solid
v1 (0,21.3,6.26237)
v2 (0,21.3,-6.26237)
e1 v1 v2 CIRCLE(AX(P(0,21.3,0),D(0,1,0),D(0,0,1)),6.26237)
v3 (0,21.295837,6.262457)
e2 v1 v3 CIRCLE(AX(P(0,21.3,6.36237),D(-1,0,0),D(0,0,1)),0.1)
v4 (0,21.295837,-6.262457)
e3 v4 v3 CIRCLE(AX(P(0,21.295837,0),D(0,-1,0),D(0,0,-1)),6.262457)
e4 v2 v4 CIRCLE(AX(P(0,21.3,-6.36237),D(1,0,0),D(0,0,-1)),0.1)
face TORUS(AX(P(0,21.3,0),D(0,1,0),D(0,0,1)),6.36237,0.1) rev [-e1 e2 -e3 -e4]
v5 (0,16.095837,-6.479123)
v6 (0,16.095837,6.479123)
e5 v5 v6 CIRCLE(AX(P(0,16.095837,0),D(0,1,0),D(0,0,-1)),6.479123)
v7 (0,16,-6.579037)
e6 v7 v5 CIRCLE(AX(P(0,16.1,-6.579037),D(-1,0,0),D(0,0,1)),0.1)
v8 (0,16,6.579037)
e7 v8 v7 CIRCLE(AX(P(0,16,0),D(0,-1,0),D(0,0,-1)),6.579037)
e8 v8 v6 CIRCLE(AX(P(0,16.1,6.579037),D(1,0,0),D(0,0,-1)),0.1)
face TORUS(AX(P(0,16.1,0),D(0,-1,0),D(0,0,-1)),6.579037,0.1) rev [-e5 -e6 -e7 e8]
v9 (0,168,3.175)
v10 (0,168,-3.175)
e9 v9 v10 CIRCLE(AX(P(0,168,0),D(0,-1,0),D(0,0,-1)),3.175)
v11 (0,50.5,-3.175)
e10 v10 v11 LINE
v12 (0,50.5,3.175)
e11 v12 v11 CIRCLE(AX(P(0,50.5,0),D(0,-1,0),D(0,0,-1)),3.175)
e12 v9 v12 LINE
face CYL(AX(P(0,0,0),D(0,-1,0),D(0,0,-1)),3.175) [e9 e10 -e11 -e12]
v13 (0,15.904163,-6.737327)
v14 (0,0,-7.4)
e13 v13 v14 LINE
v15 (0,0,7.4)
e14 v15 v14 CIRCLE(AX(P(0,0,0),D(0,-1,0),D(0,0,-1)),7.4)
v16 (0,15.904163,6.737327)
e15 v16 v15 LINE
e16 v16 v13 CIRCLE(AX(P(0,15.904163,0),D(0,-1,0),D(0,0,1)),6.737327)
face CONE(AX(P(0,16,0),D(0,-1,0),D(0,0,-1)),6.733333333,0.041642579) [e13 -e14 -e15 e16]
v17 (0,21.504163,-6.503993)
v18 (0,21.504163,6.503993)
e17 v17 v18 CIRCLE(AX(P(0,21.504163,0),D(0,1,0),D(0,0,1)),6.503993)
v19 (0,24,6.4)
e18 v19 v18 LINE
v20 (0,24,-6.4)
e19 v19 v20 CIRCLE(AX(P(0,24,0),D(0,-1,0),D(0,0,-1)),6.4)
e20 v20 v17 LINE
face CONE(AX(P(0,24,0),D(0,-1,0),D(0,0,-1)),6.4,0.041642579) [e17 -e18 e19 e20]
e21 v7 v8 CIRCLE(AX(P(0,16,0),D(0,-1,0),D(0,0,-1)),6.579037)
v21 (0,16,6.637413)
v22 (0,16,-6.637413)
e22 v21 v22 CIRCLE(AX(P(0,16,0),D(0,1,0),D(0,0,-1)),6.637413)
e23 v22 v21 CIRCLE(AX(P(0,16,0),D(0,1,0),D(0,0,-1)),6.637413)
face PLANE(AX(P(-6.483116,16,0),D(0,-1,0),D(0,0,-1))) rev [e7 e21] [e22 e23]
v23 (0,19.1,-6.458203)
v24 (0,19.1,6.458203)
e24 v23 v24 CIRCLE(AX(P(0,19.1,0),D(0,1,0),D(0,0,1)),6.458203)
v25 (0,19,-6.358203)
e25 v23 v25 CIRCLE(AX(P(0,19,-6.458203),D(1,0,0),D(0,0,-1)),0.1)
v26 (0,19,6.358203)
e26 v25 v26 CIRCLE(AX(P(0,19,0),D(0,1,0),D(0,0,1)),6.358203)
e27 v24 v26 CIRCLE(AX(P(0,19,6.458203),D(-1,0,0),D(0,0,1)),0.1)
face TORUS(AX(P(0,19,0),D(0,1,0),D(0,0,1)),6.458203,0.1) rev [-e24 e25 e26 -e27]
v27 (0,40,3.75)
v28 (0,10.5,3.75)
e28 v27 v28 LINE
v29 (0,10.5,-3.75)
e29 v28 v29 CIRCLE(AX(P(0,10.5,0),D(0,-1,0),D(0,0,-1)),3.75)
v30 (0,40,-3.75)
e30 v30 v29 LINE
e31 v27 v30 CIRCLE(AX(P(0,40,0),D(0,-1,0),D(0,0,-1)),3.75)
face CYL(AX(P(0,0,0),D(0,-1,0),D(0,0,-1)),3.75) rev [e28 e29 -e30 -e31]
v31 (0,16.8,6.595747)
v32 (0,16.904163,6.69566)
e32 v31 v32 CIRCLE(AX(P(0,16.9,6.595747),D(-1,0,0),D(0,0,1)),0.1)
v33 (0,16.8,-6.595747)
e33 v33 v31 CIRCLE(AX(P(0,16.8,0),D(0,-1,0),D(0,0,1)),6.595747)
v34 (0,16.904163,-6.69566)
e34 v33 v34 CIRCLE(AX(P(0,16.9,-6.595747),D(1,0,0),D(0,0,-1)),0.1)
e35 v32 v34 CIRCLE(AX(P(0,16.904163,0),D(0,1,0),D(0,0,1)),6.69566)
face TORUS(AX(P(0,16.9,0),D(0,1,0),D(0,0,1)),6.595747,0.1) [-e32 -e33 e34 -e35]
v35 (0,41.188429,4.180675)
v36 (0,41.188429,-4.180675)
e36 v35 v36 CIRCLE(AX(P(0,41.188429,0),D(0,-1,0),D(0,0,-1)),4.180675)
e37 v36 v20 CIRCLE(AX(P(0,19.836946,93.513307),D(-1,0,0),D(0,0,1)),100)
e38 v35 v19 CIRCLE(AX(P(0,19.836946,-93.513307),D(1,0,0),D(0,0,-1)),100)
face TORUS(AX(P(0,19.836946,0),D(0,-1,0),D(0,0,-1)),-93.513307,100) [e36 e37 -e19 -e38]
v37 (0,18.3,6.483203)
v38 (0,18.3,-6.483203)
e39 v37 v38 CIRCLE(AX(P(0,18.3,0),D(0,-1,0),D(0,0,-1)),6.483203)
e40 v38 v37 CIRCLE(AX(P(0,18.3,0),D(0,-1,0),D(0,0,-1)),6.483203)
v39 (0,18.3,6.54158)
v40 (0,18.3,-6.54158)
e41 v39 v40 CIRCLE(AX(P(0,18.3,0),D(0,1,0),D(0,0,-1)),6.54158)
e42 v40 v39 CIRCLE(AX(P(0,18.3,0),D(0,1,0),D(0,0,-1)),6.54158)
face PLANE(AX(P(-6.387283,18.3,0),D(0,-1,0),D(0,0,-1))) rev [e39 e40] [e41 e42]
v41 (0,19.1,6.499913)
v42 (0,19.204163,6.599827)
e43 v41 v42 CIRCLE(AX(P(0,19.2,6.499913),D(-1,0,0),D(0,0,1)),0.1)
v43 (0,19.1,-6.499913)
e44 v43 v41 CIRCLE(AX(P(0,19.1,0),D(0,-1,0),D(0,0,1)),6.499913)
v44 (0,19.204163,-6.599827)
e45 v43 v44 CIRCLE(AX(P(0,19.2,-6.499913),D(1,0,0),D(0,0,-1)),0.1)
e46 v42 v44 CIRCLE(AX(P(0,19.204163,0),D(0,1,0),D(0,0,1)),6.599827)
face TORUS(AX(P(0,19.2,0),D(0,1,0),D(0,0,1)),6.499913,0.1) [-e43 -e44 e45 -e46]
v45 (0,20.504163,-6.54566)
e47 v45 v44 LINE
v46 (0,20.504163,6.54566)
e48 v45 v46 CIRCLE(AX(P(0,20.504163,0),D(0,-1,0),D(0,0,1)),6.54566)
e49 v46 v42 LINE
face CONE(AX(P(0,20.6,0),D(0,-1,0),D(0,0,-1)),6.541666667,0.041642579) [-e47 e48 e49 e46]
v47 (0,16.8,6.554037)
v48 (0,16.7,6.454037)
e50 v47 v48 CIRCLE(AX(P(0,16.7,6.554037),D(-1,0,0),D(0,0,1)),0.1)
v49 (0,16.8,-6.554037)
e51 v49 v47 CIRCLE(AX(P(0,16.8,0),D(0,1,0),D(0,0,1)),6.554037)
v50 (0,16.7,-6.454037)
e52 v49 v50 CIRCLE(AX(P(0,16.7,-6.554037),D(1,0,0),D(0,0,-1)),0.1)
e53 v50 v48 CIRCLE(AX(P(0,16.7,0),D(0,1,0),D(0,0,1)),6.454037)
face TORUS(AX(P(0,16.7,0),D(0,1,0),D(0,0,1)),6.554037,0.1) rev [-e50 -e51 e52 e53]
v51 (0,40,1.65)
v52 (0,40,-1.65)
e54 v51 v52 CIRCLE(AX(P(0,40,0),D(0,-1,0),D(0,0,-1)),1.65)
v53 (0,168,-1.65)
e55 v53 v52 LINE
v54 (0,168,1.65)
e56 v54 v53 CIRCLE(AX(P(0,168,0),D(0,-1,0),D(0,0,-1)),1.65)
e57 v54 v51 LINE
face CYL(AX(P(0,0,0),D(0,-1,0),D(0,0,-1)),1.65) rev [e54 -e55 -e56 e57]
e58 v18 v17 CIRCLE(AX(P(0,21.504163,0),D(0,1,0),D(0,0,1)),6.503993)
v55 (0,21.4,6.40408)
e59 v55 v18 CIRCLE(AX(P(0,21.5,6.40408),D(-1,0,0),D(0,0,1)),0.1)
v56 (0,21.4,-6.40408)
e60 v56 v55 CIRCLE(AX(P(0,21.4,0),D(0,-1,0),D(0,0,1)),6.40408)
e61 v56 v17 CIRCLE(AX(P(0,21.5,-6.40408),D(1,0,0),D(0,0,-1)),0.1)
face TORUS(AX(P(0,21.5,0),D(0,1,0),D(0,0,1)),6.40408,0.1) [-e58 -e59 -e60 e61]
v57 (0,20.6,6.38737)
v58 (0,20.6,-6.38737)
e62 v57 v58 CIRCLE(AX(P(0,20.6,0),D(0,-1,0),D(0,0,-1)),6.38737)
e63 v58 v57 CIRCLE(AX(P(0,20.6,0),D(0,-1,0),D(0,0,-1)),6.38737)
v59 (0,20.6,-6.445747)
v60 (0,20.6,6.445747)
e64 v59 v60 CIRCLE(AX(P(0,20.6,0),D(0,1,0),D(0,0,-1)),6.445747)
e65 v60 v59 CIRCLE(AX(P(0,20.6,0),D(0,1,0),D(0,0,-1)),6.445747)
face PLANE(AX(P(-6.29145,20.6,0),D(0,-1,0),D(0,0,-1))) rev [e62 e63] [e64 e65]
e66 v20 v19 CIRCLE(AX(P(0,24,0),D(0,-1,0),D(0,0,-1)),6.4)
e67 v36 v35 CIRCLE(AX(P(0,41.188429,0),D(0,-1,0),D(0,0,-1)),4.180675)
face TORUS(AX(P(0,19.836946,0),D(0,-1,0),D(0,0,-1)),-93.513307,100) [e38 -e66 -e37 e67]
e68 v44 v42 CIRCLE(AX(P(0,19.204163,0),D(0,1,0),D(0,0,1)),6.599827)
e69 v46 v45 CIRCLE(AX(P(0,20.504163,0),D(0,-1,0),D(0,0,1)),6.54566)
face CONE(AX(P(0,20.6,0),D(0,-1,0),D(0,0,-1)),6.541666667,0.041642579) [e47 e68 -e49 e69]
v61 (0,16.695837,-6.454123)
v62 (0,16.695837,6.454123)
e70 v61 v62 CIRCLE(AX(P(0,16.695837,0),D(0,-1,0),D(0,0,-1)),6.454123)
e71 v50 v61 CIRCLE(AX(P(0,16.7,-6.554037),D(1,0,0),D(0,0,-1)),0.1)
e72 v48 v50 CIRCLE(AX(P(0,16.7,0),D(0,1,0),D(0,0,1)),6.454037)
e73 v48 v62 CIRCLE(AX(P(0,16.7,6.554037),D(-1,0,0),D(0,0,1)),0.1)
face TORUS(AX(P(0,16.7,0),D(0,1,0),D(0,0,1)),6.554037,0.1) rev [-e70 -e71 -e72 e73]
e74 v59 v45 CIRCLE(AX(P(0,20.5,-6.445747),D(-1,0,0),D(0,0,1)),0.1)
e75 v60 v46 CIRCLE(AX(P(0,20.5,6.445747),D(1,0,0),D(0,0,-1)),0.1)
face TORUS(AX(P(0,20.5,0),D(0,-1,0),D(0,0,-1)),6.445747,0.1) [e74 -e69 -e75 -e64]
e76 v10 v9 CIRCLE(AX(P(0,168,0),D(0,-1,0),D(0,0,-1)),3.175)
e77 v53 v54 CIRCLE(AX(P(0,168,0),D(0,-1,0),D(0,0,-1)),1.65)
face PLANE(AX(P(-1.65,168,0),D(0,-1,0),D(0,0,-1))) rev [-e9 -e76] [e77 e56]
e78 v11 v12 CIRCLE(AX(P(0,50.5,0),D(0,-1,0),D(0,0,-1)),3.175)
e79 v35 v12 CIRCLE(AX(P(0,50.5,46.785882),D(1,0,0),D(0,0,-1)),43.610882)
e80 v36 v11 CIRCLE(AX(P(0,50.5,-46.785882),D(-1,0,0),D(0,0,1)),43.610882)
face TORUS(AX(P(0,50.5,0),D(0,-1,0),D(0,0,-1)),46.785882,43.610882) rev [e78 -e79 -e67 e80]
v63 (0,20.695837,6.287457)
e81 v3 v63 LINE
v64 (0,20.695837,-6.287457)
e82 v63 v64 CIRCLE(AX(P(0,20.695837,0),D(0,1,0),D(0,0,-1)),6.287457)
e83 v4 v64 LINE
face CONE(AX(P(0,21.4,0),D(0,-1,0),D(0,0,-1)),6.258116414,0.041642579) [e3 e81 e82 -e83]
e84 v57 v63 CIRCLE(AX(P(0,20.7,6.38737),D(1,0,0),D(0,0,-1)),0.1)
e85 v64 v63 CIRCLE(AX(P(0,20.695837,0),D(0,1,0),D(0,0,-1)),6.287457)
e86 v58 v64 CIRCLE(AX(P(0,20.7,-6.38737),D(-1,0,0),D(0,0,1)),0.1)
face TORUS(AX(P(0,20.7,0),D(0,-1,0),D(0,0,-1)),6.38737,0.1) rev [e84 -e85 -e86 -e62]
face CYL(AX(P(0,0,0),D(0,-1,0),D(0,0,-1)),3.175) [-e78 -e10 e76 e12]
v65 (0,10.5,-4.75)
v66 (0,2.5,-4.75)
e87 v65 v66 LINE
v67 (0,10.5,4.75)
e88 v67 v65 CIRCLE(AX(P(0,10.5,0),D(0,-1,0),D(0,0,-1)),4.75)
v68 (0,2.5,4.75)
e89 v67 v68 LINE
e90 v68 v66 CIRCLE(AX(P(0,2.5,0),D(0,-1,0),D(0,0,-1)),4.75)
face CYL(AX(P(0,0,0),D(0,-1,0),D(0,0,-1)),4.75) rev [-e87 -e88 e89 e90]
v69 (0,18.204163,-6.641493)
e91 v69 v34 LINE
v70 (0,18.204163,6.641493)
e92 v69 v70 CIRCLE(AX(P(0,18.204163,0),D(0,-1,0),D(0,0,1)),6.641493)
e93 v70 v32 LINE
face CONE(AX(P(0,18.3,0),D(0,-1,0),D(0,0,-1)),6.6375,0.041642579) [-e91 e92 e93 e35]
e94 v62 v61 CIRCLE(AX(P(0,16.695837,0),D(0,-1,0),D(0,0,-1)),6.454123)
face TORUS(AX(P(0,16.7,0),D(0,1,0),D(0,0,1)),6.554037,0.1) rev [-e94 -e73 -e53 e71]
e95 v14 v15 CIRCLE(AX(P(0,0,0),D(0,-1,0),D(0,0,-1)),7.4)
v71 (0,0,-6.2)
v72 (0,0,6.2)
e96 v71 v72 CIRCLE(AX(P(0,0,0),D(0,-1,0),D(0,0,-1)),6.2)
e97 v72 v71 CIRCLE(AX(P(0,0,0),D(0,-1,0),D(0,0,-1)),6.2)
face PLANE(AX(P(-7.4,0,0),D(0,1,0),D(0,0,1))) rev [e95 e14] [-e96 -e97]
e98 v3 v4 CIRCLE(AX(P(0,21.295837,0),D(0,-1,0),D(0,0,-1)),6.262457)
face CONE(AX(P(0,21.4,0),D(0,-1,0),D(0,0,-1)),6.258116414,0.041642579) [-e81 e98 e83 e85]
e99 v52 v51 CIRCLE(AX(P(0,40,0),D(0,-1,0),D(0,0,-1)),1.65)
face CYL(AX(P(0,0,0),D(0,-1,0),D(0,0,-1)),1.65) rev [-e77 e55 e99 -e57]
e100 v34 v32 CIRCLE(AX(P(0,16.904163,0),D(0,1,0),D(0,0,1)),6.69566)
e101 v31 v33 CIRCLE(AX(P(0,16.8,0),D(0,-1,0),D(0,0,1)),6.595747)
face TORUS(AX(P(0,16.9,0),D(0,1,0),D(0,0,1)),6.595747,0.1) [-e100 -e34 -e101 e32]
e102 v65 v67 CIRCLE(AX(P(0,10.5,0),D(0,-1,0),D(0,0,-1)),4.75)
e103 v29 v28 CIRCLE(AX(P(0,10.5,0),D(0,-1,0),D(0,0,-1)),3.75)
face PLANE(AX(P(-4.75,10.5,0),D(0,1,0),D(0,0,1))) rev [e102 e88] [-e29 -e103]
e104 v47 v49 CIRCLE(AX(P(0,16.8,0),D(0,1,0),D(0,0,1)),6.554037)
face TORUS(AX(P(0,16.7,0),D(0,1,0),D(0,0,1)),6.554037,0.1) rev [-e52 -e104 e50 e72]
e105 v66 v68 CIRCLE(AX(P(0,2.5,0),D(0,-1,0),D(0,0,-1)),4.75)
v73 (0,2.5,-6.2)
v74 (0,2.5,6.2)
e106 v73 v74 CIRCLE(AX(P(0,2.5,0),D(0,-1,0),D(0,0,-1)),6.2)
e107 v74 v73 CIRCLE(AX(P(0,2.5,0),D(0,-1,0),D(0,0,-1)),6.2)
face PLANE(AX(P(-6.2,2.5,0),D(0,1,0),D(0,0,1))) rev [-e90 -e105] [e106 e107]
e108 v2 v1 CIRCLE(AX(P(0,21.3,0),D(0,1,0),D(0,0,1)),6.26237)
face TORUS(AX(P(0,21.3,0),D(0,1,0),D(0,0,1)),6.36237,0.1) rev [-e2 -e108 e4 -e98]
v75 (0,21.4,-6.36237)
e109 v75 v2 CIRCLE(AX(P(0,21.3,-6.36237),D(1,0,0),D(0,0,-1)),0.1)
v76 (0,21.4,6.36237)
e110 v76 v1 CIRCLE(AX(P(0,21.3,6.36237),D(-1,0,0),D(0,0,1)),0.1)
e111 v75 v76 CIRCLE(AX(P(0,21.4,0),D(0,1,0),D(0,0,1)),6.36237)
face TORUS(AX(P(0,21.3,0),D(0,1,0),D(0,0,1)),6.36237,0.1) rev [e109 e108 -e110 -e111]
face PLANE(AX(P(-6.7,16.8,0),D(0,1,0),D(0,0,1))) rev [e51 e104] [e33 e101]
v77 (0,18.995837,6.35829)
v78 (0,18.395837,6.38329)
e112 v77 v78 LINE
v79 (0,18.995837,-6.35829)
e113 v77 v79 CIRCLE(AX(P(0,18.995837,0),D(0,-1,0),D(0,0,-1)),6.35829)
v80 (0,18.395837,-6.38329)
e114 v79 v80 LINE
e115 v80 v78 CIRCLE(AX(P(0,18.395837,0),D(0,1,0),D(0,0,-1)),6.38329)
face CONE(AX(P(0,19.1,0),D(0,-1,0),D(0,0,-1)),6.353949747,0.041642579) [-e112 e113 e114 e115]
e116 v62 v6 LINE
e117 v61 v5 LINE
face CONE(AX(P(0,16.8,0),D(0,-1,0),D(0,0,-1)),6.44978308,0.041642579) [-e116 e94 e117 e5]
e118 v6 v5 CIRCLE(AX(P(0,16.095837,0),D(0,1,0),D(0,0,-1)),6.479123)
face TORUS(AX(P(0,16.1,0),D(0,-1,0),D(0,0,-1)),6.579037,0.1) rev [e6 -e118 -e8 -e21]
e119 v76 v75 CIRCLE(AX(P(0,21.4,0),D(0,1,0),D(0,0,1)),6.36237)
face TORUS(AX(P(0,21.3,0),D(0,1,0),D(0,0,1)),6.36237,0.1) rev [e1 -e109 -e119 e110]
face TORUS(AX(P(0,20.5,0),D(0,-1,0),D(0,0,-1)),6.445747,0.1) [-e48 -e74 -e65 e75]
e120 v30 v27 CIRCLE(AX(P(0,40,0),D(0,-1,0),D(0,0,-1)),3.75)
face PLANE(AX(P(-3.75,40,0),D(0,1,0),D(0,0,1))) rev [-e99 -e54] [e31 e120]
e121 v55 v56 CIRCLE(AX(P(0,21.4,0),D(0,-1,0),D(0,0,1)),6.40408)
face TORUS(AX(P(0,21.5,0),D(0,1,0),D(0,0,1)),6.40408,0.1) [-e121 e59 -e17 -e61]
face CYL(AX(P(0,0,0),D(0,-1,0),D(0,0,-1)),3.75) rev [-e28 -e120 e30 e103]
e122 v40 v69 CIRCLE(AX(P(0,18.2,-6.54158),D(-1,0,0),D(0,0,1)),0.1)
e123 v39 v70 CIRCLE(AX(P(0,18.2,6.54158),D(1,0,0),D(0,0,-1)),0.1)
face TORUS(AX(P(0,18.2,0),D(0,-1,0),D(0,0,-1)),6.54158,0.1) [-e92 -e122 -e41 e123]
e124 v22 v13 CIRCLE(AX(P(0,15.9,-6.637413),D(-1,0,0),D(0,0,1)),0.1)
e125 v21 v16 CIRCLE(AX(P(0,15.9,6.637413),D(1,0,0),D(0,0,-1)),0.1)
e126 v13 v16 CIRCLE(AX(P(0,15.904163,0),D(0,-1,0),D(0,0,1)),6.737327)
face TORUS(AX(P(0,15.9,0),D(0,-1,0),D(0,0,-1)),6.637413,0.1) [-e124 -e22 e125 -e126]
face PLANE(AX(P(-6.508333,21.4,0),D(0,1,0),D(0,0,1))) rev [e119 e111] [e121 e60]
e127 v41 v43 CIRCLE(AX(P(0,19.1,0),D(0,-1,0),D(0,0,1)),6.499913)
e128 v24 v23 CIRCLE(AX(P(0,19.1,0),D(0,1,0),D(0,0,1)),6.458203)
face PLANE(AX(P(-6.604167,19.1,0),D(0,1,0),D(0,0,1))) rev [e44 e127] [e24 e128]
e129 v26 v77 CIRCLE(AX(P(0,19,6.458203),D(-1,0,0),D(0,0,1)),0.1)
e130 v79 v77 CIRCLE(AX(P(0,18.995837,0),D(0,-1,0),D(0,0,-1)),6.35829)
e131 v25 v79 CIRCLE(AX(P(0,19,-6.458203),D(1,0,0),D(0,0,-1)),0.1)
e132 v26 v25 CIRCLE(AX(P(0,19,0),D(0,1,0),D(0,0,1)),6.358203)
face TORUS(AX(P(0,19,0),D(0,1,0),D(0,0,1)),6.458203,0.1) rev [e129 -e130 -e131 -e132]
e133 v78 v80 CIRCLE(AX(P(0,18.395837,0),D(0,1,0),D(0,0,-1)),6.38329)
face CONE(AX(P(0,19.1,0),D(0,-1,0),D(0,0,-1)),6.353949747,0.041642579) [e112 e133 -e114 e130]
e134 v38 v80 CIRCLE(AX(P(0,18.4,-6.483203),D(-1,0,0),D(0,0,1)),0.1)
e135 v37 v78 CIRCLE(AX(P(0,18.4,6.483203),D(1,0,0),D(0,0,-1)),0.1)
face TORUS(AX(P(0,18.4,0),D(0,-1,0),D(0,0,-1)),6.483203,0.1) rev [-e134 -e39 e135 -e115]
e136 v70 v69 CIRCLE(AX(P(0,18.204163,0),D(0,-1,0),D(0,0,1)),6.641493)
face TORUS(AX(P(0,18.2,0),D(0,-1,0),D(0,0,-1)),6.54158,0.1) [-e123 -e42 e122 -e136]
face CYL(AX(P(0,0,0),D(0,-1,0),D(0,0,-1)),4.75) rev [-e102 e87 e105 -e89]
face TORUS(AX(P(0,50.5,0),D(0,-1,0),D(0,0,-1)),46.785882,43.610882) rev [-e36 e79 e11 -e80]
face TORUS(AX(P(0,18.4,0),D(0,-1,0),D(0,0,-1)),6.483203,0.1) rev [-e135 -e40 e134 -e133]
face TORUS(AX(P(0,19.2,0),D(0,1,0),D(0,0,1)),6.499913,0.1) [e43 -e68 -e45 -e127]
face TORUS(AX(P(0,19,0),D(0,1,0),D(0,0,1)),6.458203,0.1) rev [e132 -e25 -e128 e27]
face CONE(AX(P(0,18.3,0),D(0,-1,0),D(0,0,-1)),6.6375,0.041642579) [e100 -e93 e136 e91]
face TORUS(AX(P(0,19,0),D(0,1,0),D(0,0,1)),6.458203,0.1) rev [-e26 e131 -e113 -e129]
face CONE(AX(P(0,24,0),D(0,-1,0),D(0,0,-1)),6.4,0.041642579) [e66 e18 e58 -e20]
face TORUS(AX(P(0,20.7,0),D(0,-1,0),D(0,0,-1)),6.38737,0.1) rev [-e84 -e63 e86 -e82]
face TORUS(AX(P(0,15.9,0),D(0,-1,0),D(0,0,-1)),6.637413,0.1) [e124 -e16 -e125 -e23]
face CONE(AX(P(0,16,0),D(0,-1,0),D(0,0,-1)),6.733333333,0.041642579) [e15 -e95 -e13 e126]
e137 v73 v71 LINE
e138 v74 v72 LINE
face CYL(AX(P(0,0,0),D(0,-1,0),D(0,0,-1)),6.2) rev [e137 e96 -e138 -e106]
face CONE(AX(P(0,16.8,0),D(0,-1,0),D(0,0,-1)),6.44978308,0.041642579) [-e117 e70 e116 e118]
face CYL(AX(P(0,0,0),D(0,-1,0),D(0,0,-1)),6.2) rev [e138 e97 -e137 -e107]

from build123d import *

# Parameters (mm, degrees)
FILLET_3_R = 0.1


with BuildPart() as part:
    # 草图1 → 旋转1 (revolve)
    with BuildSketch(Plane.XY, mode=Mode.PRIVATE) as revolve_1_sk:
        with BuildLine():
            Line((-7.4, 0), (-6.733333333, 16))
            Line((-6.733333333, 16), (-6.483116414, 16))
            Line((-6.483116414, 16), (-6.44978308, 16.8))
            Line((-6.44978308, 16.8), (-6.7, 16.8))
            Line((-6.7, 16.8), (-6.6375, 18.3))
            Line((-6.6375, 18.3), (-6.38728308, 18.3))
            Line((-6.38728308, 18.3), (-6.353949747, 19.1))
            Line((-6.353949747, 19.1), (-6.604166667, 19.1))
            Line((-6.604166667, 19.1), (-6.541666667, 20.6))
            Line((-6.541666667, 20.6), (-6.291449747, 20.6))
            Line((-6.291449747, 20.6), (-6.258116414, 21.4))
            Line((-6.258116414, 21.4), (-6.508333333, 21.4))
            Line((-6.508333333, 21.4), (-6.4, 24))
            ThreePointArc((-6.4, 24), (-5.663407353, 32.642384563), (-4.180674763, 41.18842948))
            ThreePointArc((-4.180674763, 41.18842948), (-3.427147619, 45.817139569), (-3.175, 50.5))
            Line((-3.175, 50.5), (-3.175, 168))
            Line((-3.175, 168), (-1.65, 168))
            Line((-1.65, 168), (-1.65, 40))
            Line((-1.65, 40), (-3.75, 40))
            Line((-3.75, 40), (-3.75, 10.5))
            Line((-3.75, 10.5), (-4.75, 10.5))
            Line((-4.75, 10.5), (-4.75, 2.5))
            Line((-4.75, 2.5), (-6.2, 2.5))
            Line((-6.2, 2.5), (-6.2, 0))
            Line((-6.2, 0), (-7.4, 0))
        make_face()
    revolve(revolve_1_sk.sketch.rotate(Axis((0, 0, 0), (0, 1, 0)), 270), axis=Axis((0, 0, 0), (0, 1, 0)))

    # 圆角3
    fillet_3_edges = [part.edges().sort_by_distance(p)[0] for p in [
        (0, 16, 6.733333333),
        (0, 16, 6.483116414),
        (0, 16.8, 6.44978308),
        (0, 16.8, 6.7),
        (0, 18.3, 6.6375),
        (0, 18.3, 6.38728308),
        (0, 19.1, 6.353949747),
        (0, 19.1, 6.604166667),
        (0, 20.6, 6.541666667),
        (0, 20.6, 6.291449747),
        (0, 21.4, 6.258116414),
        (0, 21.4, 6.508333333),
    ]]
    fillet(fillet_3_edges, radius=FILLET_3_R)


solid = part.part
